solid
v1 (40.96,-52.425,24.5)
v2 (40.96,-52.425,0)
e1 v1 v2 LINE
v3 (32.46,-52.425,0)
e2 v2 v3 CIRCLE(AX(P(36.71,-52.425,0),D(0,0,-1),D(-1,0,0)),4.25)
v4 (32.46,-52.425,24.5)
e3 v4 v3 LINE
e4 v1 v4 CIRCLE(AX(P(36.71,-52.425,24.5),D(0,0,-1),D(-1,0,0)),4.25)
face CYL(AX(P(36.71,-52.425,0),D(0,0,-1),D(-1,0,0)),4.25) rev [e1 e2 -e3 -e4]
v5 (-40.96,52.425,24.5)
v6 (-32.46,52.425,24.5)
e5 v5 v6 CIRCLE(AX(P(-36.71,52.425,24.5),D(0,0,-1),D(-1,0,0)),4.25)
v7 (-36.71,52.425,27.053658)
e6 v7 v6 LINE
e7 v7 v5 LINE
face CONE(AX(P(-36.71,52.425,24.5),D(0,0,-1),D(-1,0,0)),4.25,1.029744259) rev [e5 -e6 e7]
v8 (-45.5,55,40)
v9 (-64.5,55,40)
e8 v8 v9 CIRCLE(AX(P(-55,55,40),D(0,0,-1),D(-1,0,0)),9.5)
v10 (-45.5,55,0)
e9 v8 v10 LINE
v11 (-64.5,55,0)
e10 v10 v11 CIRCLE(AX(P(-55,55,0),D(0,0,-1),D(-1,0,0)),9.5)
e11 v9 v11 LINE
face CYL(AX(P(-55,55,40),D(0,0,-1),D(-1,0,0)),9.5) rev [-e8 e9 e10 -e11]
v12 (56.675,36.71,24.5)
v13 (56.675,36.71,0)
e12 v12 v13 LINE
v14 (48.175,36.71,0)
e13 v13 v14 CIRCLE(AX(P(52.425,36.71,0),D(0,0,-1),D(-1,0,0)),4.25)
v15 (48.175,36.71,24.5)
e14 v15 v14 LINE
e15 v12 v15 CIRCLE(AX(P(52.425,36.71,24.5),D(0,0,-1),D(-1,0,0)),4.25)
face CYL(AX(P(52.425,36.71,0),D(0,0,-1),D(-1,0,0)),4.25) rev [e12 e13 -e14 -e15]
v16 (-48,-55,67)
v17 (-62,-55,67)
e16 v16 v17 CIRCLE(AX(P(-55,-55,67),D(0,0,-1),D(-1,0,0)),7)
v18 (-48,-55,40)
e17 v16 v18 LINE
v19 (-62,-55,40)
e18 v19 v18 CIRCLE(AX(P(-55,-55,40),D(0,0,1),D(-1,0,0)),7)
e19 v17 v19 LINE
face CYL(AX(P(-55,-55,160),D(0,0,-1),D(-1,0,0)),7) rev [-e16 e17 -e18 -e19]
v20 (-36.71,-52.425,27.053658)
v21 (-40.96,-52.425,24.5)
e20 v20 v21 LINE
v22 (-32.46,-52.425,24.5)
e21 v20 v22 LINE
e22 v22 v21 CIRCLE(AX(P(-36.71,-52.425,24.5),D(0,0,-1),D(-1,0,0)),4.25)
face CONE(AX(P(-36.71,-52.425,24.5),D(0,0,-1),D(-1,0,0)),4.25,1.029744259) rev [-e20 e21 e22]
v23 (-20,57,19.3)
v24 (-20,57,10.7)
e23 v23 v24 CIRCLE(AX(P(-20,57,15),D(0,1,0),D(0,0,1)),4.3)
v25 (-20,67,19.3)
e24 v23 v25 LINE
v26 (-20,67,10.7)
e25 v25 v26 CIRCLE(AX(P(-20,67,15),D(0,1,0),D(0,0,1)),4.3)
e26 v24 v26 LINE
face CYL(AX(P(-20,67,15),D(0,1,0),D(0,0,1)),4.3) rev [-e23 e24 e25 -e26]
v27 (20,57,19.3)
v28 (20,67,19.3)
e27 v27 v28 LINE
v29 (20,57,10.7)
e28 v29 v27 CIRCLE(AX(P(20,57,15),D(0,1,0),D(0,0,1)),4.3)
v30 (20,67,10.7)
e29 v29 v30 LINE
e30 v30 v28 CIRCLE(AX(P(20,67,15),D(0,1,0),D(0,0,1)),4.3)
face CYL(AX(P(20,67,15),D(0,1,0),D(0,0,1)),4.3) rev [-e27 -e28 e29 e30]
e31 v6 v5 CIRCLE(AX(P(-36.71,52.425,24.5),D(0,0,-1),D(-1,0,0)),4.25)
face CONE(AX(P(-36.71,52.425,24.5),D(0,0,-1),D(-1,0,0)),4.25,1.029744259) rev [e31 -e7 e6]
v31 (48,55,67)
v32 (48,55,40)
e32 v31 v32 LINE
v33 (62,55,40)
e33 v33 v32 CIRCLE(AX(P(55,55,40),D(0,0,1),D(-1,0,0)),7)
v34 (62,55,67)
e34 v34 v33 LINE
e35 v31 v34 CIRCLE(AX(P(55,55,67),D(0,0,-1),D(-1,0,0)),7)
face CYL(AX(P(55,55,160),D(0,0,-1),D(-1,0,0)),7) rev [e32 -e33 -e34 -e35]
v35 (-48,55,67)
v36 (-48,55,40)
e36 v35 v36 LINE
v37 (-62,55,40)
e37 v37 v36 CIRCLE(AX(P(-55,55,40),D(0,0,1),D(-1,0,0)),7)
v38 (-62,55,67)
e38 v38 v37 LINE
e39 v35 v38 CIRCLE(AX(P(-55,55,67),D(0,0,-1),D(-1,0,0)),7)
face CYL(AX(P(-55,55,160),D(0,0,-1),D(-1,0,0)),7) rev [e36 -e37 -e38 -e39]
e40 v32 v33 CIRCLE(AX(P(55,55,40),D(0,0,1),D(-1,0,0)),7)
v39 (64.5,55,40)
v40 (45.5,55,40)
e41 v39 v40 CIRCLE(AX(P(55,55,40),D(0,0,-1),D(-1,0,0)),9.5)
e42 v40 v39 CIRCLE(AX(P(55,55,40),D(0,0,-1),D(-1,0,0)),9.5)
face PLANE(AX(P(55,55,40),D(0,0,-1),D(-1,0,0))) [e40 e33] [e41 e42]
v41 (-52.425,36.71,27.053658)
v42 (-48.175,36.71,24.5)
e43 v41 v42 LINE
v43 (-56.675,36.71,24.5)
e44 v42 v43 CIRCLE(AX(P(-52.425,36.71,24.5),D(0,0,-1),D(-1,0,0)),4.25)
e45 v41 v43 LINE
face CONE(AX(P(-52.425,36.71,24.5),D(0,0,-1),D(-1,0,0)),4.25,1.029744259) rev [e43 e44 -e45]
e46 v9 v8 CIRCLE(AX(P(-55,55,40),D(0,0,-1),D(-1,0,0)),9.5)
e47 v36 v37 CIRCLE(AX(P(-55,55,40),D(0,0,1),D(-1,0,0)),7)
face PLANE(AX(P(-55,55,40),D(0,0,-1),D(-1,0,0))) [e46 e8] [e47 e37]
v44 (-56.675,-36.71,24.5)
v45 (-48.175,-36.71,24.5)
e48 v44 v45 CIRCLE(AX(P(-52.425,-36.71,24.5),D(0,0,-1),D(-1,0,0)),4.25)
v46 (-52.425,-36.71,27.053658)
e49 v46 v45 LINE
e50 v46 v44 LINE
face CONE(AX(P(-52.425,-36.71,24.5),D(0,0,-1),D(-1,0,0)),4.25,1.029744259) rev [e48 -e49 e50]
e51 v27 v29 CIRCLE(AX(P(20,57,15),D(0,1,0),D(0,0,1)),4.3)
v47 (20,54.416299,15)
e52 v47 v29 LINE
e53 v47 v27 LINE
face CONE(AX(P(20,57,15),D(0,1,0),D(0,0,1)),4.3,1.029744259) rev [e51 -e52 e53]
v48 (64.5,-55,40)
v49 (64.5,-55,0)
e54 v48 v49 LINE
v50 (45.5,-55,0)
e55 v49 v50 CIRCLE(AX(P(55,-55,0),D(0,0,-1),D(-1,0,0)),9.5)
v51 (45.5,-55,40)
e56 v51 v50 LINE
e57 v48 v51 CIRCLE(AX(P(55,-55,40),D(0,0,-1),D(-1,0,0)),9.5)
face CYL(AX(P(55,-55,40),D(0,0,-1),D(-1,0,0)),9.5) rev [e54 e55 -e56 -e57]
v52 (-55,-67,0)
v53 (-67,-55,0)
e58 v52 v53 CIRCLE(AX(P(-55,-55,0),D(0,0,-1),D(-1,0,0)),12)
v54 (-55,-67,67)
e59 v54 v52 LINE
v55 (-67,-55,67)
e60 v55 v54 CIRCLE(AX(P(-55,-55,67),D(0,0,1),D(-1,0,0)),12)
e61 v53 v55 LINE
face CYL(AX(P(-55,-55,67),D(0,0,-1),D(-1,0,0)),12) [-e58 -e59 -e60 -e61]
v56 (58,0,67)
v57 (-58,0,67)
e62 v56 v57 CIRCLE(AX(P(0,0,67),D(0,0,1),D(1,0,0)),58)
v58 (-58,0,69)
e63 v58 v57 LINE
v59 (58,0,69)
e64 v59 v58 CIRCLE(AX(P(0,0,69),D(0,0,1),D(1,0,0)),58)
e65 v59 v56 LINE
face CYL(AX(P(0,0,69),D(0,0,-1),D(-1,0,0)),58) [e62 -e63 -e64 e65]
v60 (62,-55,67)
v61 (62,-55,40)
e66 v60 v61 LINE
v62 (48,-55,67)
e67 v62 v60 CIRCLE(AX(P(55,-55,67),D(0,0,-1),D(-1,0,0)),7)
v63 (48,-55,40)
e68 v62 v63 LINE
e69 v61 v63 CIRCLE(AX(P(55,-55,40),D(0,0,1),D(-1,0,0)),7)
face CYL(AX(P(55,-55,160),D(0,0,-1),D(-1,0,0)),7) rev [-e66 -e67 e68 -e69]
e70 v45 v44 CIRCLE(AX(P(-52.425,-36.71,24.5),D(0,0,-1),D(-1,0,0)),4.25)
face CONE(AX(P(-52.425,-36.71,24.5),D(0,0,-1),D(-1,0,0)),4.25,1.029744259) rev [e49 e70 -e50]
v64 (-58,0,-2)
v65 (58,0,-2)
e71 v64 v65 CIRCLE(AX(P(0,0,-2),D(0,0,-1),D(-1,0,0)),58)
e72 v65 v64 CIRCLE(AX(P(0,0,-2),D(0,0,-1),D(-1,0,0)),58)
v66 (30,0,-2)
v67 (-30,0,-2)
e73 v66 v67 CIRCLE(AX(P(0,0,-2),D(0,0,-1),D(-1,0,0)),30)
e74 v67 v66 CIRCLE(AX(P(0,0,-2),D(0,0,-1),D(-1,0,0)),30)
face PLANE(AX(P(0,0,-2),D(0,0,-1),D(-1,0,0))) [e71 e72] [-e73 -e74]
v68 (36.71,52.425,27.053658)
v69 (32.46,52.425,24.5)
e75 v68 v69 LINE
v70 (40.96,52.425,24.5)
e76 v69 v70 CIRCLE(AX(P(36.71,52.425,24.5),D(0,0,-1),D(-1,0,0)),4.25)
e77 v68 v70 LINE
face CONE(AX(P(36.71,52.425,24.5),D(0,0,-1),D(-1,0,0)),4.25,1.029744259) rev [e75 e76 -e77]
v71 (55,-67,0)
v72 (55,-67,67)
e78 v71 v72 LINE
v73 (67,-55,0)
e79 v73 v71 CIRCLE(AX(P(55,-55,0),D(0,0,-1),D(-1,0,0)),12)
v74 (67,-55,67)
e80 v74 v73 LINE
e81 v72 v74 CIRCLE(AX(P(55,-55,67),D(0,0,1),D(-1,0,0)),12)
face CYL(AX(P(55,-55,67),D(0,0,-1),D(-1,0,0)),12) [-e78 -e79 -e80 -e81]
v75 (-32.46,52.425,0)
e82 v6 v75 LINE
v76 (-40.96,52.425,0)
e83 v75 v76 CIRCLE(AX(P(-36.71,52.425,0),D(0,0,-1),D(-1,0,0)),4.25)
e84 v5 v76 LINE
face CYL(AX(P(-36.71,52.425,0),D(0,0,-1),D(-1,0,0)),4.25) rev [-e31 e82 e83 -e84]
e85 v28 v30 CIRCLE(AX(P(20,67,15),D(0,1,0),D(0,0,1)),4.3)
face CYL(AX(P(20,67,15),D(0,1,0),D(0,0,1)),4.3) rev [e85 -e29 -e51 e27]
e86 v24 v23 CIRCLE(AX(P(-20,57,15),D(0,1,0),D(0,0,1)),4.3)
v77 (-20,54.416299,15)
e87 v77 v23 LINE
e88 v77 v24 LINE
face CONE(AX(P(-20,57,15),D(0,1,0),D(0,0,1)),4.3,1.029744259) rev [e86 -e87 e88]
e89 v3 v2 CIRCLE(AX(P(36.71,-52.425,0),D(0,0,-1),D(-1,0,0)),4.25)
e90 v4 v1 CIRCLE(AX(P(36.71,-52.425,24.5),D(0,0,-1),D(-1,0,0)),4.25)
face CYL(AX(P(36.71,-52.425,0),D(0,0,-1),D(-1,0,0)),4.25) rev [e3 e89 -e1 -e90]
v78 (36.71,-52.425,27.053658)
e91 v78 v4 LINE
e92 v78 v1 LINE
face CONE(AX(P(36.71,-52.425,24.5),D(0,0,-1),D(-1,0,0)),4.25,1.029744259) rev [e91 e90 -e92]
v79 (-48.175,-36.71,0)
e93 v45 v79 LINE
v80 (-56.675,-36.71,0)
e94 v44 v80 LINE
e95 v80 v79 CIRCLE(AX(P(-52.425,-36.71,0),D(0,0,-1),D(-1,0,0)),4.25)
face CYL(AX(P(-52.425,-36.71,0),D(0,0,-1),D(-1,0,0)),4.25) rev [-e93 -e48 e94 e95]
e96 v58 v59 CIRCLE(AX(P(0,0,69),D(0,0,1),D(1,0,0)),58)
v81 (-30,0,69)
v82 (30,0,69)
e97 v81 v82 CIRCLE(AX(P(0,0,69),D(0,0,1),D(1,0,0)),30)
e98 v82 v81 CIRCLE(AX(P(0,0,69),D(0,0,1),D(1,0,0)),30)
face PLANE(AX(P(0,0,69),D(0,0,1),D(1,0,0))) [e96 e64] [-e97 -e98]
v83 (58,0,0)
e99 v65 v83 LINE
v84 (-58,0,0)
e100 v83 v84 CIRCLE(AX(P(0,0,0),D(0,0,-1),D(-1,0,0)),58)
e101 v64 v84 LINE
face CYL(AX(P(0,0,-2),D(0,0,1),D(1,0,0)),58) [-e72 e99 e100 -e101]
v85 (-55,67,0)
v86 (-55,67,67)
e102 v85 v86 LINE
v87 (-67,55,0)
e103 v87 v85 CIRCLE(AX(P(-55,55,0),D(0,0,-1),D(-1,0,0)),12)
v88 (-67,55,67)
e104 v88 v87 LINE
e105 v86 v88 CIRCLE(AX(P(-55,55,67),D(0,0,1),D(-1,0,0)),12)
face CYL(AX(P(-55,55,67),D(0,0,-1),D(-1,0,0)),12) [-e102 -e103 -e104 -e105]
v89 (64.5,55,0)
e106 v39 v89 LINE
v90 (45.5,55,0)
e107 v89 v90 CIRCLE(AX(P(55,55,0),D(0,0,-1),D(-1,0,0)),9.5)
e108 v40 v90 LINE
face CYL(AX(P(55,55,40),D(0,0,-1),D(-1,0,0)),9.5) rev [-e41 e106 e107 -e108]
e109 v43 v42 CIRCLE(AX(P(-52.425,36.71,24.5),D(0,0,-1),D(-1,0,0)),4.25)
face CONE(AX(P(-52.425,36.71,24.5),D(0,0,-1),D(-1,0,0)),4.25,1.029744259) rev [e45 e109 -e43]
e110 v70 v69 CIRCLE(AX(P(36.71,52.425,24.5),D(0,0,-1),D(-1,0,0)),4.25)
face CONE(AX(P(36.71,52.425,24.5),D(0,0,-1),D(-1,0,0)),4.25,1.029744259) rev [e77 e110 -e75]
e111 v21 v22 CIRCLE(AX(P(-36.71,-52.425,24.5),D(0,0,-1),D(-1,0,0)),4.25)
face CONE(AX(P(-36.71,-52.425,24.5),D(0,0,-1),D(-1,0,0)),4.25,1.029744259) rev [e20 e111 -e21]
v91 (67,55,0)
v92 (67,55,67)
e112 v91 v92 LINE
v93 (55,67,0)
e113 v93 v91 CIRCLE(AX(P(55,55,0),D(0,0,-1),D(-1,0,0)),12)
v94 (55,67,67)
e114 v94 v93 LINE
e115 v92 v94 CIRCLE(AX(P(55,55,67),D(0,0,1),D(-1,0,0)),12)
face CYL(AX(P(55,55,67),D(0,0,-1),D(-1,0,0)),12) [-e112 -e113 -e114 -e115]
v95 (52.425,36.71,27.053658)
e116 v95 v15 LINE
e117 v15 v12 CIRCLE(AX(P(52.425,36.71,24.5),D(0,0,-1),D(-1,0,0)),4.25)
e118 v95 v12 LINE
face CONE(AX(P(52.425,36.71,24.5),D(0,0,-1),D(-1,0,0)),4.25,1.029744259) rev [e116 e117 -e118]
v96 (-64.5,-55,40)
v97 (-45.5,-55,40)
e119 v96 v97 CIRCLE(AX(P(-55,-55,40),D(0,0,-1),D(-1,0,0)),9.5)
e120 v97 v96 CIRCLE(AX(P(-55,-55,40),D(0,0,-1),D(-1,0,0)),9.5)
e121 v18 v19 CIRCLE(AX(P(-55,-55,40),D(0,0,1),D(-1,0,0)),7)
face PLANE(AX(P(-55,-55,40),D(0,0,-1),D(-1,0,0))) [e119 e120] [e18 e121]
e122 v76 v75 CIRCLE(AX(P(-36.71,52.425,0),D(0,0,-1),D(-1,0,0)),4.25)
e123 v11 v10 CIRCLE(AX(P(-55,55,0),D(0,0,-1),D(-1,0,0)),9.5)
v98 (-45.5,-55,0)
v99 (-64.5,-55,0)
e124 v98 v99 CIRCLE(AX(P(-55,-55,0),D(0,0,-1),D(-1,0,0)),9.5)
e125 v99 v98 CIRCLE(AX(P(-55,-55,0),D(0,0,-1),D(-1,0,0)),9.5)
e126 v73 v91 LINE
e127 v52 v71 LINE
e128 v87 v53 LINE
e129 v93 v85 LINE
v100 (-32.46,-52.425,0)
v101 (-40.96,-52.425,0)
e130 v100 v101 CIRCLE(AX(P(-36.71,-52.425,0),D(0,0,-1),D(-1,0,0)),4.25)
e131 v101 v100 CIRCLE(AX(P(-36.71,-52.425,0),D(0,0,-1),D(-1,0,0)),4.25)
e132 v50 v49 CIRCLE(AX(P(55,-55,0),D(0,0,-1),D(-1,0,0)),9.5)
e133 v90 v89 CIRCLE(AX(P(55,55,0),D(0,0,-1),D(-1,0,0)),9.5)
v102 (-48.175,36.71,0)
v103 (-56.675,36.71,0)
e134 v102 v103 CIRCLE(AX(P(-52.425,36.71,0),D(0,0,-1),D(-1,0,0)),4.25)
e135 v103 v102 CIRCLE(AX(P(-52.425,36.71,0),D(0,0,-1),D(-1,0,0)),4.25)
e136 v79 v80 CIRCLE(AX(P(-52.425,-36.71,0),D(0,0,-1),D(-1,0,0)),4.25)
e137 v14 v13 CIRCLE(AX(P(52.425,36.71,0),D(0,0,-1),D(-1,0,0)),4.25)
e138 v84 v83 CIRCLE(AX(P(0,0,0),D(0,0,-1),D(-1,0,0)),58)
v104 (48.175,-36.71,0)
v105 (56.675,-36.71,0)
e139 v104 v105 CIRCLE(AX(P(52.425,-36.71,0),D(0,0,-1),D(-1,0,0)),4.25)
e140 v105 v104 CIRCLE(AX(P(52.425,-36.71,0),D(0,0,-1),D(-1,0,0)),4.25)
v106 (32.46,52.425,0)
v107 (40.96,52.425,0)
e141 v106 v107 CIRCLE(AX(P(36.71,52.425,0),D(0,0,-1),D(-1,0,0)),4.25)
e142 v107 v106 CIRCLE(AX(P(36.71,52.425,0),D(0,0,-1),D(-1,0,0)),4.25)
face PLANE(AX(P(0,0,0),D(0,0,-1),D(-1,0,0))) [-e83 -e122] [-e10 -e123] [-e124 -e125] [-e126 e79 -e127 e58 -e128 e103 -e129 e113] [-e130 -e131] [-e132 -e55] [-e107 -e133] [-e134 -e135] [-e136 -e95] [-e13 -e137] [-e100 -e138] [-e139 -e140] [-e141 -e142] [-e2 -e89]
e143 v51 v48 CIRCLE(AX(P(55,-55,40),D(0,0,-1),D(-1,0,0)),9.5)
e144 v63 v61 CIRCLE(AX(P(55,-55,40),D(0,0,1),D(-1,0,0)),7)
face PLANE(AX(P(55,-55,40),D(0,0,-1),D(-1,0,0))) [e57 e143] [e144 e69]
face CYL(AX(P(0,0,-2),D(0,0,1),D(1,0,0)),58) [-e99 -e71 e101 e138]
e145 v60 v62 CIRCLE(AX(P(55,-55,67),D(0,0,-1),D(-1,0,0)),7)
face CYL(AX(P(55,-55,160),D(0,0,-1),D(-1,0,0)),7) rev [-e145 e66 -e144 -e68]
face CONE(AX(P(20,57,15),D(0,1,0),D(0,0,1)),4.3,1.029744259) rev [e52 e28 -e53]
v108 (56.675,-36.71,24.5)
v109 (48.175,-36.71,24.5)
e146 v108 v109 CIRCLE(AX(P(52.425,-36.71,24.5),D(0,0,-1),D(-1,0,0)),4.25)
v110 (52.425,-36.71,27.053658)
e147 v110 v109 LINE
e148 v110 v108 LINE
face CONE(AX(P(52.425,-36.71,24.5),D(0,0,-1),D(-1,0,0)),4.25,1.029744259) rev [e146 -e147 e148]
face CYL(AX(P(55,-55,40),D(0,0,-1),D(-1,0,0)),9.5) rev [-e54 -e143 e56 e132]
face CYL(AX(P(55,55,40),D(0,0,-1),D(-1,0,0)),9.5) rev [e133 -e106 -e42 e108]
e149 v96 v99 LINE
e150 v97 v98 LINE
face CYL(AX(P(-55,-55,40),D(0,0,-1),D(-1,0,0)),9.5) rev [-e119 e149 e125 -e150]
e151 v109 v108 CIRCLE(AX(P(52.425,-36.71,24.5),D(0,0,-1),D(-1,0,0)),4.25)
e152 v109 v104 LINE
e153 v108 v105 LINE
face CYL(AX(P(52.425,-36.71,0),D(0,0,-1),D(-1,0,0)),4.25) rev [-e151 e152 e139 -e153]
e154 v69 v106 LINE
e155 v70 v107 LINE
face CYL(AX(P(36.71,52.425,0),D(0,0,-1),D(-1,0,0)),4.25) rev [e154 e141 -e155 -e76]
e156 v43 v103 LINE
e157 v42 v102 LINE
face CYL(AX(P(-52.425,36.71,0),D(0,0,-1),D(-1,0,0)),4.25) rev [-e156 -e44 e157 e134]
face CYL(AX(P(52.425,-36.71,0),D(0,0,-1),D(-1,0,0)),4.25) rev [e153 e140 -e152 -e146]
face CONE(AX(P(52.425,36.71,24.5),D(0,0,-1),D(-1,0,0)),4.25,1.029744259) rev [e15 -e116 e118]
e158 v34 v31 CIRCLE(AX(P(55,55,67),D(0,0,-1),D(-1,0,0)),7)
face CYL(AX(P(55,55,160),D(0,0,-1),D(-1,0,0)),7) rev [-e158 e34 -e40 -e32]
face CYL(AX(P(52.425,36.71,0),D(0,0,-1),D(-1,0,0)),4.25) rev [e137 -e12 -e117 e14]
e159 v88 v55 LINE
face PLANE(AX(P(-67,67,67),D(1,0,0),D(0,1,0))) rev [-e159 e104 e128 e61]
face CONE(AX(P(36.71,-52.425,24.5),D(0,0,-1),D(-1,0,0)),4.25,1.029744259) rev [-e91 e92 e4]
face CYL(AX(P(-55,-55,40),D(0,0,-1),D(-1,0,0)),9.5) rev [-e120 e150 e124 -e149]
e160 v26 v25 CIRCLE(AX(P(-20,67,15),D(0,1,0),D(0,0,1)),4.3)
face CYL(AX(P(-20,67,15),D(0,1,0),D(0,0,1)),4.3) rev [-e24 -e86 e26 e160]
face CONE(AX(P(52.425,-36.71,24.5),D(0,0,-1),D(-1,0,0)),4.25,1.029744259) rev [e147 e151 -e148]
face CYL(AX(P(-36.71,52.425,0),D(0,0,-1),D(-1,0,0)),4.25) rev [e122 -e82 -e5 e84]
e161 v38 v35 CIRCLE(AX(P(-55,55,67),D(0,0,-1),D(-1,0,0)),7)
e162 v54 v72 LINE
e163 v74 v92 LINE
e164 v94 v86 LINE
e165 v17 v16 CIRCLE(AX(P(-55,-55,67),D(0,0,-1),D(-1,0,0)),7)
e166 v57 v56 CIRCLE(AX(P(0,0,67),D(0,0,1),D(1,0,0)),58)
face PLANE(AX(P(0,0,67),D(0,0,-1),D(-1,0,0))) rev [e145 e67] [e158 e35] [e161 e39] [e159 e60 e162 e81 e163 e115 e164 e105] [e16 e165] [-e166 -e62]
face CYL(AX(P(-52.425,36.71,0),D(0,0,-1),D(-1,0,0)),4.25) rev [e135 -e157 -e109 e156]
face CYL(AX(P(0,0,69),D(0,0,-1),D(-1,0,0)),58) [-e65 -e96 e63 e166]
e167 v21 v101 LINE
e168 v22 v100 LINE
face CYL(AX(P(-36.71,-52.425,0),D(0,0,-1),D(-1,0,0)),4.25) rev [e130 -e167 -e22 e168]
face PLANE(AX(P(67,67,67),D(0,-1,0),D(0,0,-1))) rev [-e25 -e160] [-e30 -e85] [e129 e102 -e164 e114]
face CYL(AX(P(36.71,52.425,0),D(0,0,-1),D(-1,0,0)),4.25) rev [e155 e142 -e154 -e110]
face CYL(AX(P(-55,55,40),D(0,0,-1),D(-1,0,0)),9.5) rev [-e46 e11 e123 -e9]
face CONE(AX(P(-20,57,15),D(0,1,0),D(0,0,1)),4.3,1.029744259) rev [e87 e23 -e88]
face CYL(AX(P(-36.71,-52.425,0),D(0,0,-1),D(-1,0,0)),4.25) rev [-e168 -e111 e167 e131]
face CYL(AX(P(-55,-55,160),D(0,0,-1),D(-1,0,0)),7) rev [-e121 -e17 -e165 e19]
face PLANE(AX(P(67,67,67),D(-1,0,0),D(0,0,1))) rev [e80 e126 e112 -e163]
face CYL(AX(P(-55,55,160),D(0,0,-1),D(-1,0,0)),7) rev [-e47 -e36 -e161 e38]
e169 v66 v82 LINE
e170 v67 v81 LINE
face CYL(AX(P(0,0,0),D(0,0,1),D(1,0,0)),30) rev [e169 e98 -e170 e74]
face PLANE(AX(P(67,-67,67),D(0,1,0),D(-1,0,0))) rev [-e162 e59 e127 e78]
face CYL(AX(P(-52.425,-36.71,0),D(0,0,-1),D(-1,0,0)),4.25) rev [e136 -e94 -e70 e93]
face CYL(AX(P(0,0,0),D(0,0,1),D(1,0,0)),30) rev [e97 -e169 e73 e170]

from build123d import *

# Parameters (mm, degrees)
SKETCH1_W                  = 134
SKETCH1_H                  = 134
BOSS_EXTRUDE1_DEPTH        = 67
FILLET1_R                  = 12
SKETCH2_R                  = 30
CUT_EXTRUDE1_DEPTH         = 67
BOSS_EXTRUDE2_START        = 2
SKETCH3_R                  = 58
SKETCH3_R_2                = 30
BOSS_EXTRUDE2_DEPTH        = 2
SKETCH4_R                  = 58
SKETCH4_R_2                = 30
BOSS_EXTRUDE3_DEPTH        = 2
SKETCH5_R                  = 7
CUT_EXTRUDE2_DEPTH         = 160
SKETCH6_R                  = 9.5
CUT_EXTRUDE3_DEPTH         = 40
SIZE_MM_DOWEL_HOLE_1_D     = 8.5
SIZE_MM_DOWEL_HOLE_1_DEPTH = 24.5
SIZE_MM_DOWEL_HOLE_1_TIP   = 2.553657631
SIZE_MM_DOWEL_HOLE_2_D     = 8.5
SIZE_MM_DOWEL_HOLE_2_DEPTH = 24.5
SIZE_MM_DOWEL_HOLE_2_TIP   = 2.553657631
SIZE_MM_DOWEL_HOLE_3_D     = 8.6
SIZE_MM_DOWEL_HOLE_3_DEPTH = 10
SIZE_MM_DOWEL_HOLE_3_TIP   = 2.583700662


with BuildPart() as part:
    # Sketch1 → Boss-Extrude1 (new body)
    with BuildSketch(Plane.XY):
        Rectangle(SKETCH1_W, SKETCH1_H)
    extrude(amount=BOSS_EXTRUDE1_DEPTH)

    # Fillet1
    fillet1_edges = [part.edges().sort_by_distance(p)[0] for p in [
        (-67, 67, 33.5),
        (67, 67, 33.5),
        (67, -67, 33.5),
        (-67, -67, 33.5),
    ]]
    fillet(fillet1_edges, radius=FILLET1_R)

    # Sketch2 → Cut-Extrude1 (cut)
    with BuildSketch(Plane.XY.offset(67)):
        Circle(SKETCH2_R)
    extrude(amount=-CUT_EXTRUDE1_DEPTH, mode=Mode.SUBTRACT)

    # Sketch3 → Boss-Extrude2 (add)
    with BuildSketch(Plane.XY.offset(67).offset(BOSS_EXTRUDE2_START)):
        Circle(SKETCH3_R)
        Circle(SKETCH3_R_2, mode=Mode.SUBTRACT)
    extrude(amount=-BOSS_EXTRUDE2_DEPTH)

    # Sketch4 → Boss-Extrude3 (add)
    with BuildSketch(Plane(origin=(0, 0, 0), x_dir=(-1, 0, 0), z_dir=(0, 0, -1))):
        with Locations(Location((0, 0, 0), (0, 0, 180))):
            Circle(SKETCH4_R)
        with Locations(Location((0, 0, 0), (0, 0, 180))):
            Circle(SKETCH4_R_2, mode=Mode.SUBTRACT)
    extrude(amount=BOSS_EXTRUDE3_DEPTH)

    # Sketch5 → Cut-Extrude2 (cut)
    with BuildSketch(Plane(origin=(0, 0, 0), x_dir=(-1, 0, 0), z_dir=(0, 0, -1))):
        with Locations((-55, 55)):
            Circle(SKETCH5_R)
        with Locations((55, 55)):
            Circle(SKETCH5_R)
        with Locations((55, -55)):
            Circle(SKETCH5_R)
        with Locations((-55, -55)):
            Circle(SKETCH5_R)
    extrude(amount=-CUT_EXTRUDE2_DEPTH, mode=Mode.SUBTRACT)

    # Sketch6 → Cut-Extrude3 (cut)
    with BuildSketch(Plane(origin=(0, 0, 0), x_dir=(-1, 0, 0), z_dir=(0, 0, -1))):
        with Locations((-55, 55)):
            Circle(SKETCH6_R)
        with Locations((55, 55)):
            Circle(SKETCH6_R)
        with Locations((55, -55)):
            Circle(SKETCH6_R)
        with Locations((-55, -55)):
            Circle(SKETCH6_R)
    extrude(amount=-CUT_EXTRUDE3_DEPTH, mode=Mode.SUBTRACT)

    # Size mm Dowel hole 1
    with Locations(Plane(origin=(0, 0, 0), x_dir=(-1, 0, 0), z_dir=(0, 0, -1))):
        with Locations((-36.71, 52.425), (36.71, 52.425), (36.71, -52.425), (-36.71, -52.425)):
            Hole(SIZE_MM_DOWEL_HOLE_1_D / 2, depth=SIZE_MM_DOWEL_HOLE_1_DEPTH)
            with Locations((0, 0, -(SIZE_MM_DOWEL_HOLE_1_DEPTH + SIZE_MM_DOWEL_HOLE_1_TIP / 2))):  # 118° drill point
                Cone(0, SIZE_MM_DOWEL_HOLE_1_D / 2, SIZE_MM_DOWEL_HOLE_1_TIP, mode=Mode.SUBTRACT)

    # Size mm Dowel hole 2
    with Locations(Plane(origin=(0, 0, 0), x_dir=(-1, 0, 0), z_dir=(0, 0, -1))):
        with Locations((-52.425, 36.71), (52.425, 36.71), (52.425, -36.71), (-52.425, -36.71)):
            Hole(SIZE_MM_DOWEL_HOLE_2_D / 2, depth=SIZE_MM_DOWEL_HOLE_2_DEPTH)
            with Locations((0, 0, -(SIZE_MM_DOWEL_HOLE_2_DEPTH + SIZE_MM_DOWEL_HOLE_2_TIP / 2))):  # 118° drill point
                Cone(0, SIZE_MM_DOWEL_HOLE_2_D / 2, SIZE_MM_DOWEL_HOLE_2_TIP, mode=Mode.SUBTRACT)

    # Size mm Dowel hole 3
    with Locations(Plane(origin=(0, 67, 0), x_dir=(1, 0, 0), z_dir=(0, 1, 0))):
        with Locations((-20, -15), (20, -15)):
            Hole(SIZE_MM_DOWEL_HOLE_3_D / 2, depth=SIZE_MM_DOWEL_HOLE_3_DEPTH)
            with Locations((0, 0, -(SIZE_MM_DOWEL_HOLE_3_DEPTH + SIZE_MM_DOWEL_HOLE_3_TIP / 2))):  # 118° drill point
                Cone(0, SIZE_MM_DOWEL_HOLE_3_D / 2, SIZE_MM_DOWEL_HOLE_3_TIP, mode=Mode.SUBTRACT)


solid = part.part
